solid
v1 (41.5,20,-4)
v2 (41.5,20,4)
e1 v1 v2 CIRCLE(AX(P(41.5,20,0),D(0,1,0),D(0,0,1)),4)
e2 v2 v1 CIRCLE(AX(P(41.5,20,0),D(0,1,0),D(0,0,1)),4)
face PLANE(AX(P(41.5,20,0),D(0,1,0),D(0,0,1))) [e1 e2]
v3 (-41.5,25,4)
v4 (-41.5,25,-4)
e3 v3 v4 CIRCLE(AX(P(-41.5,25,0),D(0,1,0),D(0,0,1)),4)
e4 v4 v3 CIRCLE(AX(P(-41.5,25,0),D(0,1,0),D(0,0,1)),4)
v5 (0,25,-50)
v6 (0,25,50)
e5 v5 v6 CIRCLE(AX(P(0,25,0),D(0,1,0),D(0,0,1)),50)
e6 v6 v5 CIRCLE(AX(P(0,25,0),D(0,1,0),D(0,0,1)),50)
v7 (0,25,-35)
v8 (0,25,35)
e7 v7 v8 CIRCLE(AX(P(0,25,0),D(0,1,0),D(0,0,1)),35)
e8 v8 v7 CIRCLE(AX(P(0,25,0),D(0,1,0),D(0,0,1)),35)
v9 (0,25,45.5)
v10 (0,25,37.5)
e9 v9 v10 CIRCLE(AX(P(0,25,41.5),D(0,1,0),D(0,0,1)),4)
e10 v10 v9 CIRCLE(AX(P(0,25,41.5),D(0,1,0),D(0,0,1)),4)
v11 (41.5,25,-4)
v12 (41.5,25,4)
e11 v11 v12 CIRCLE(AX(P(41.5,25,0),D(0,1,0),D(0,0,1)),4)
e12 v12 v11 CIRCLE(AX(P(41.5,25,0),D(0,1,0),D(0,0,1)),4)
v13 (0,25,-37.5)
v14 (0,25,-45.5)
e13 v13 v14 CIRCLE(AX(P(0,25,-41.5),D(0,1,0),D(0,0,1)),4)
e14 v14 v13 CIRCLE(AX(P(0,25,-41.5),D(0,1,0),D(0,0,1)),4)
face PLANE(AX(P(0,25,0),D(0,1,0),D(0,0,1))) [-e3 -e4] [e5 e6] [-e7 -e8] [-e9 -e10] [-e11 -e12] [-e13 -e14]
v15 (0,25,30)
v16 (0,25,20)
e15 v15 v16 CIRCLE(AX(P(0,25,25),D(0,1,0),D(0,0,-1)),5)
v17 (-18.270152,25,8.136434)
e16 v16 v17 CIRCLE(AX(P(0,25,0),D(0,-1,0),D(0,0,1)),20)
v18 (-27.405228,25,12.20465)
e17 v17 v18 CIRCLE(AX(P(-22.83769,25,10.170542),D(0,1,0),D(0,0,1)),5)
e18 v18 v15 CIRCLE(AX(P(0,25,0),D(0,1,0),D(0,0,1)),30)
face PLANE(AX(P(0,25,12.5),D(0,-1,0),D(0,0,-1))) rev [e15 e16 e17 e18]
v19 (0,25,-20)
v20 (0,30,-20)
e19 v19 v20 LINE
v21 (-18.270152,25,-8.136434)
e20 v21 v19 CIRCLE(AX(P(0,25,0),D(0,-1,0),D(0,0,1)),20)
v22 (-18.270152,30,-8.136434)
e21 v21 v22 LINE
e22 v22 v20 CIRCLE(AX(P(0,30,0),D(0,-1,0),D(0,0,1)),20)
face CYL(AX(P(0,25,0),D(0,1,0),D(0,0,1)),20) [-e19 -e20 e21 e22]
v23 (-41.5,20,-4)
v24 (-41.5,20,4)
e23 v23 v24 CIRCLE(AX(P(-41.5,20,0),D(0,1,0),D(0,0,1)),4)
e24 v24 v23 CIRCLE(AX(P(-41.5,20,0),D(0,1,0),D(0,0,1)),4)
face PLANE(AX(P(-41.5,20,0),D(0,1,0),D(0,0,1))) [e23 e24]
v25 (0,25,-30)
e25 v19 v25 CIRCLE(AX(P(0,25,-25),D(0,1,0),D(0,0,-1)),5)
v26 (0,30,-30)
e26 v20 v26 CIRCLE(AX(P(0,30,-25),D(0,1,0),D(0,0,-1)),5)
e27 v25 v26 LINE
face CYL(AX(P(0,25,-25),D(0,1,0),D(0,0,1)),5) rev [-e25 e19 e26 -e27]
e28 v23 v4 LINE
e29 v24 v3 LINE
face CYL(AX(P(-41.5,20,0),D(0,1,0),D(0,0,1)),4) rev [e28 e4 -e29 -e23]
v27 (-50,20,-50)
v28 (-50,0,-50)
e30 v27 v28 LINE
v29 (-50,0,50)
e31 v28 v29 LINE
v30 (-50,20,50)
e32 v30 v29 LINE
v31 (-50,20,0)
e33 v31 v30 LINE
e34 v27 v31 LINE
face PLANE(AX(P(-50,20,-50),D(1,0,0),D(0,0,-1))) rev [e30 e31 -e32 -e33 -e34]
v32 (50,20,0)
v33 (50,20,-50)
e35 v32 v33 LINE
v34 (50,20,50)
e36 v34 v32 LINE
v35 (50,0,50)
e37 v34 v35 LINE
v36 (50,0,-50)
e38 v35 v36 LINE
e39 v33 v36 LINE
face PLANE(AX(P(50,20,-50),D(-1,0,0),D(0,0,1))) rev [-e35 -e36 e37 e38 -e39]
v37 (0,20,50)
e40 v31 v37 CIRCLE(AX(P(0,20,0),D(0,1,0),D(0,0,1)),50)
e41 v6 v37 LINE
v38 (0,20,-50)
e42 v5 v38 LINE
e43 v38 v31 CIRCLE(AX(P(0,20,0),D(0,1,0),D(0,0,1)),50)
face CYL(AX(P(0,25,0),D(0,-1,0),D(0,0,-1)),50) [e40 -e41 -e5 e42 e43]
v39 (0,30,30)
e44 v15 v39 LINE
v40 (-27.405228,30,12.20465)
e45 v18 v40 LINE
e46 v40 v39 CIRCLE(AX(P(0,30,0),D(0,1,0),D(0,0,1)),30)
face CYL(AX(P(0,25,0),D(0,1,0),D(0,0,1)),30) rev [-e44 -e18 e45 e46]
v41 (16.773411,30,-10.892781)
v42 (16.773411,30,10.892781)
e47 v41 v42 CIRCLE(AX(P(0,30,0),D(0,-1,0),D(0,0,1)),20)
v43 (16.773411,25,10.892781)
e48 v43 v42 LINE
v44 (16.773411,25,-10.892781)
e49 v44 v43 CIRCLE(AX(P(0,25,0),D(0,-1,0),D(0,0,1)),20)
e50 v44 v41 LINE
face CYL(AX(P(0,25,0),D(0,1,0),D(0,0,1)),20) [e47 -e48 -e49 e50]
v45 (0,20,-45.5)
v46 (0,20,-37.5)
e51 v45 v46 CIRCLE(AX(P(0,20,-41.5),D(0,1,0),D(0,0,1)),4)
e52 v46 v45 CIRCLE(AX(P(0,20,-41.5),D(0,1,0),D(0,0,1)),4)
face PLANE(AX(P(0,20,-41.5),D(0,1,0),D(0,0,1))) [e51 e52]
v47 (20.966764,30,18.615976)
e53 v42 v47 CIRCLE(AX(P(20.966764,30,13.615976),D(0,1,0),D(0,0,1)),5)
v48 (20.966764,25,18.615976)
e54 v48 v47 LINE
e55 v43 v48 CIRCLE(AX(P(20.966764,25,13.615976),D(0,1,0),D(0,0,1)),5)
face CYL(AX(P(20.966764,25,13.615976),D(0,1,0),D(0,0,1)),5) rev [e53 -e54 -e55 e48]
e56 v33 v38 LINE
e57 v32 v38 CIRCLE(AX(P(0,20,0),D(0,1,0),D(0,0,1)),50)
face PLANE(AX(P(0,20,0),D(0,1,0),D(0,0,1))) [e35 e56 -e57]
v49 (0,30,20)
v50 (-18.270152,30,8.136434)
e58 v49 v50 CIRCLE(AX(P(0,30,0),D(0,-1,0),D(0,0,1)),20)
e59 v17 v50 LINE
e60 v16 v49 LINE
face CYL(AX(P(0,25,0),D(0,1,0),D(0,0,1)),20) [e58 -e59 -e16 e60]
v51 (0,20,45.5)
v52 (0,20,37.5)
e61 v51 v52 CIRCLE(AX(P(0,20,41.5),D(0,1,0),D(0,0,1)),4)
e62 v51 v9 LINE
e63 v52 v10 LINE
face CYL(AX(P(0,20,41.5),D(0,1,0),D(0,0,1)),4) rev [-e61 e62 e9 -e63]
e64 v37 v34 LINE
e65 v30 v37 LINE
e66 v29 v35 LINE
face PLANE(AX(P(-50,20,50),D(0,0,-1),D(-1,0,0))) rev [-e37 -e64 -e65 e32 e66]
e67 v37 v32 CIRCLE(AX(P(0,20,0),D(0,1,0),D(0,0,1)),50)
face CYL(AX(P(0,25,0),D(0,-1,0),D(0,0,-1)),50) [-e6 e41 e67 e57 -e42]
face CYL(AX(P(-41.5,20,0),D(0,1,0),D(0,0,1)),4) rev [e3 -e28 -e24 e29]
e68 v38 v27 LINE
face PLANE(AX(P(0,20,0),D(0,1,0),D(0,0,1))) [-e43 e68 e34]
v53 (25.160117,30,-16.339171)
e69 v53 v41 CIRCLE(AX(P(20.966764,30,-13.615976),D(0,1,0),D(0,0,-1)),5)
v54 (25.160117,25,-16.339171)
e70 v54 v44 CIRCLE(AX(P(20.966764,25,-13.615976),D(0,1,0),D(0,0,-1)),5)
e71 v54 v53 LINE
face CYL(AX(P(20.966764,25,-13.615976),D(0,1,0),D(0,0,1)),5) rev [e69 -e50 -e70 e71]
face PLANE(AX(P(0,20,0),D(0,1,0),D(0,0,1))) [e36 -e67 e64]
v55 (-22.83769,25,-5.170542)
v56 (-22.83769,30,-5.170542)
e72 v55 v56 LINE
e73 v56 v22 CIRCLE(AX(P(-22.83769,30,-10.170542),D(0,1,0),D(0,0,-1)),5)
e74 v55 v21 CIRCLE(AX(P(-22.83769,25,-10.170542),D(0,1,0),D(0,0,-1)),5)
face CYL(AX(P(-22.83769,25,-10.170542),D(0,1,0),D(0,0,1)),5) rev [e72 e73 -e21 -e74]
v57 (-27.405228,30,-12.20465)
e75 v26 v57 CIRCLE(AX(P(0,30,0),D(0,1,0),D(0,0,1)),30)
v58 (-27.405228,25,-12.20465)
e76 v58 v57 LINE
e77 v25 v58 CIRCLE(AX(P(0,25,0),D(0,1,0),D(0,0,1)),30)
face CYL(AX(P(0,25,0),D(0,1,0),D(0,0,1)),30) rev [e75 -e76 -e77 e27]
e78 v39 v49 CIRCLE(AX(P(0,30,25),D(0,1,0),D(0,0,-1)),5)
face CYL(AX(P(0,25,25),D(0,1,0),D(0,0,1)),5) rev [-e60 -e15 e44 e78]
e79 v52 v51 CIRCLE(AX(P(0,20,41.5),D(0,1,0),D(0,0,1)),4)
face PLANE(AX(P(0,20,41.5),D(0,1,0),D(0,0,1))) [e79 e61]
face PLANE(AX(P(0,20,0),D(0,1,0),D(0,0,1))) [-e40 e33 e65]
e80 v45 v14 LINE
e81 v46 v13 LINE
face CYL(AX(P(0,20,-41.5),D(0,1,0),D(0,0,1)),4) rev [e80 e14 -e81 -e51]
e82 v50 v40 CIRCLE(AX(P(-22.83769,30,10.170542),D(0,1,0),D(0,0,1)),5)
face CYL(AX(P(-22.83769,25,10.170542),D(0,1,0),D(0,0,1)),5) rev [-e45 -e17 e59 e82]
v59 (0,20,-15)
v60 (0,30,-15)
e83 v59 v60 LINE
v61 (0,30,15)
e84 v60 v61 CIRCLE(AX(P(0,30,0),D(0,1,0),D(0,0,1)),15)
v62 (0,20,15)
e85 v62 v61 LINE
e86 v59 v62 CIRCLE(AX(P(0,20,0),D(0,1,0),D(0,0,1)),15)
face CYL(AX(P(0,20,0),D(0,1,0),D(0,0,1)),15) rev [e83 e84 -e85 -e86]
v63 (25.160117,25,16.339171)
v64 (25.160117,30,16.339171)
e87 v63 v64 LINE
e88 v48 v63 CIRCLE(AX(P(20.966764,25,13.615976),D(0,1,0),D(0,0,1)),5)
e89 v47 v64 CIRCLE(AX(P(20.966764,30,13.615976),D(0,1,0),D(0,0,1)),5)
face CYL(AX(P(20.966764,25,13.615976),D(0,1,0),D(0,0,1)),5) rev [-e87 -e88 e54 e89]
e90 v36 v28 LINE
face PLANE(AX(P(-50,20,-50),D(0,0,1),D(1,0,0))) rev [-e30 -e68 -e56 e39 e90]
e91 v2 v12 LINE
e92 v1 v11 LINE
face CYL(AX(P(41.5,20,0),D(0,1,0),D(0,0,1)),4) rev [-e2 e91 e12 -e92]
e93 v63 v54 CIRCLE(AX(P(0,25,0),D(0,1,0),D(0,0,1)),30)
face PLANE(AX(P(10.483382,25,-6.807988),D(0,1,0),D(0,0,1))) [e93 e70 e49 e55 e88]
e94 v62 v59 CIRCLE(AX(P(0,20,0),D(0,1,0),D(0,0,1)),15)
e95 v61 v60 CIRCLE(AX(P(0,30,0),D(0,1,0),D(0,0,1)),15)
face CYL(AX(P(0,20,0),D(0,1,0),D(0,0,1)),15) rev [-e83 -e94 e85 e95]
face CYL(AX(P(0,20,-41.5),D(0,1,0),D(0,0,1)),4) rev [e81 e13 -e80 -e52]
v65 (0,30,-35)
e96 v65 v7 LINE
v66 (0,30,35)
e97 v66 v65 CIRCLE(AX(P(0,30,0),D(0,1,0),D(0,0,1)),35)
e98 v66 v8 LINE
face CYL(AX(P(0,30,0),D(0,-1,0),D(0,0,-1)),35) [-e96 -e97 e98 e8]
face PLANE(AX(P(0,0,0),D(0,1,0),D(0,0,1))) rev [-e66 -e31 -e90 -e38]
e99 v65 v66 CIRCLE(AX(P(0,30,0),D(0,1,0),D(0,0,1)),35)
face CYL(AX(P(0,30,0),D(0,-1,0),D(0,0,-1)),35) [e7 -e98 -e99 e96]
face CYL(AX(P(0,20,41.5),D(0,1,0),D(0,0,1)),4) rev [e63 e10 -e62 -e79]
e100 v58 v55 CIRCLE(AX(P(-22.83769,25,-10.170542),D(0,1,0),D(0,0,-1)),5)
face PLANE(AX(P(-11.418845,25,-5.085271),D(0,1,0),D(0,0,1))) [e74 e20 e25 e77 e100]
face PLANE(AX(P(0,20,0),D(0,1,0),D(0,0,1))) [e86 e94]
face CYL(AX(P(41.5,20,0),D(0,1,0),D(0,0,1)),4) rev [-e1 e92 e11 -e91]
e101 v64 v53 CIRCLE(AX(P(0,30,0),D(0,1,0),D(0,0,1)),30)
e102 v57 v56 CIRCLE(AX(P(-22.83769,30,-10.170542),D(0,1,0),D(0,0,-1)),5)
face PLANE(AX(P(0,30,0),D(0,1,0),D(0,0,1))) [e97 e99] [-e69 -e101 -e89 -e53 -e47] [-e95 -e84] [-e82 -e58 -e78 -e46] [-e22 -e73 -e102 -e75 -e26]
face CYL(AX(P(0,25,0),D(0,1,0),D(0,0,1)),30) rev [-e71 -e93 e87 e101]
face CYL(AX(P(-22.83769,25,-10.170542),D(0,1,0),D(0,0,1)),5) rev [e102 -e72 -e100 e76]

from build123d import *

# Parameters (mm, degrees)
BASE_PLATE_SKETCH_W     = 100
BASE_PLATE_SKETCH_H     = 100
BASE_PLATE_DEPTH        = 20
FLANGE_DISC_SKETCH_R    = 50
FLANGE_DISC_DEPTH       = 5
FLANGE_HOLES_SKETCH_R   = 4
FLANGE_HOLES_4X_8_DEPTH = 5
HUB_DISC_SKETCH_R       = 35
HUB_DISC_DEPTH          = 5
ARC_SLOTS_3X_DEPTH      = 5
CENTRE_BORE_SKETCH_R    = 15
CENTRE_BORE_DEPTH       = 10


with BuildPart() as part:
    # Base Plate Sketch → Base Plate (new body)
    with BuildSketch(Plane(origin=(0, 0, 0), x_dir=(1, 0, 0), z_dir=(0, 1, 0))):
        Rectangle(BASE_PLATE_SKETCH_W, BASE_PLATE_SKETCH_H)
    extrude(amount=BASE_PLATE_DEPTH)

    # Flange Disc Sketch → Flange Disc (add)
    with BuildSketch(Plane(origin=(0, 20, 0), x_dir=(1, 0, 0), z_dir=(0, 1, 0))):
        with Locations(Location((0, 0, 0), (0, 0, 270))):
            Circle(FLANGE_DISC_SKETCH_R)
    extrude(amount=FLANGE_DISC_DEPTH)

    # Flange Holes Sketch → Flange Holes 4xØ8 (cut)
    with BuildSketch(Plane(origin=(0, 25, 0), x_dir=(1, 0, 0), z_dir=(0, 1, 0))):
        with Locations(Location((0, 41.5, 0), (0, 0, 270))):
            Circle(FLANGE_HOLES_SKETCH_R)
        with Locations(Location((41.5, 0, 0), (0, 0, 270))):
            Circle(FLANGE_HOLES_SKETCH_R)
        with Locations(Location((0, -41.5, 0), (0, 0, 270))):
            Circle(FLANGE_HOLES_SKETCH_R)
        with Locations(Location((-41.5, 0, 0), (0, 0, 270))):
            Circle(FLANGE_HOLES_SKETCH_R)
    extrude(amount=-FLANGE_HOLES_4X_8_DEPTH, mode=Mode.SUBTRACT)

    # Hub Disc Sketch → Hub Disc (add)
    with BuildSketch(Plane(origin=(0, 25, 0), x_dir=(1, 0, 0), z_dir=(0, 1, 0))):
        with Locations(Location((0, 0, 0), (0, 0, 270))):
            Circle(HUB_DISC_SKETCH_R)
    extrude(amount=HUB_DISC_DEPTH)

    # Arc Slots Sketch → Arc Slots 3x (cut)
    with BuildSketch(Plane(origin=(0, 30, 0), x_dir=(1, 0, 0), z_dir=(0, 1, 0))):
        with BuildLine():
            ThreePointArc((-27.405227761, -12.2046504), (-16.338, -25.160877489), (0, -30))
            ThreePointArc((0, -30), (5, -25), (0, -20))
            ThreePointArc((0, -20), (-10.892, -16.773918326), (-18.27015184, -8.1364336))
            ThreePointArc((-18.27015184, -8.1364336), (-24.871798201, -5.60300404), (-27.405227761, -12.2046504))
        make_face()
        with BuildLine():
            ThreePointArc((16.773411359, 10.8927807), (18.243569024, 17.809328715), (25.160117038, 16.33917105))
            ThreePointArc((25.160117038, 16.33917105), (30, 0), (25.160117038, -16.33917105))
            ThreePointArc((25.160117038, -16.33917105), (18.243569024, -17.809328715), (16.773411359, -10.8927807))
            ThreePointArc((16.773411359, -10.8927807), (20, 0), (16.773411359, 10.8927807))
        make_face()
        with BuildLine():
            ThreePointArc((0, 30), (5, 25), (0, 20))
            ThreePointArc((0, 20), (-10.892, 16.773918326), (-18.27015184, 8.1364336))
            ThreePointArc((-18.27015184, 8.1364336), (-24.871798201, 5.60300404), (-27.405227761, 12.2046504))
            ThreePointArc((-27.405227761, 12.2046504), (-16.338, 25.160877489), (0, 30))
        make_face()
    extrude(amount=-ARC_SLOTS_3X_DEPTH, mode=Mode.SUBTRACT)

    # Centre Bore Sketch → Centre Bore (cut)
    with BuildSketch(Plane(origin=(0, 30, 0), x_dir=(1, 0, 0), z_dir=(0, 1, 0))):
        with Locations(Location((0, 0, 0), (0, 0, 270))):
            Circle(CENTRE_BORE_SKETCH_R)
    extrude(amount=-CENTRE_BORE_DEPTH, mode=Mode.SUBTRACT)


solid = part.part
